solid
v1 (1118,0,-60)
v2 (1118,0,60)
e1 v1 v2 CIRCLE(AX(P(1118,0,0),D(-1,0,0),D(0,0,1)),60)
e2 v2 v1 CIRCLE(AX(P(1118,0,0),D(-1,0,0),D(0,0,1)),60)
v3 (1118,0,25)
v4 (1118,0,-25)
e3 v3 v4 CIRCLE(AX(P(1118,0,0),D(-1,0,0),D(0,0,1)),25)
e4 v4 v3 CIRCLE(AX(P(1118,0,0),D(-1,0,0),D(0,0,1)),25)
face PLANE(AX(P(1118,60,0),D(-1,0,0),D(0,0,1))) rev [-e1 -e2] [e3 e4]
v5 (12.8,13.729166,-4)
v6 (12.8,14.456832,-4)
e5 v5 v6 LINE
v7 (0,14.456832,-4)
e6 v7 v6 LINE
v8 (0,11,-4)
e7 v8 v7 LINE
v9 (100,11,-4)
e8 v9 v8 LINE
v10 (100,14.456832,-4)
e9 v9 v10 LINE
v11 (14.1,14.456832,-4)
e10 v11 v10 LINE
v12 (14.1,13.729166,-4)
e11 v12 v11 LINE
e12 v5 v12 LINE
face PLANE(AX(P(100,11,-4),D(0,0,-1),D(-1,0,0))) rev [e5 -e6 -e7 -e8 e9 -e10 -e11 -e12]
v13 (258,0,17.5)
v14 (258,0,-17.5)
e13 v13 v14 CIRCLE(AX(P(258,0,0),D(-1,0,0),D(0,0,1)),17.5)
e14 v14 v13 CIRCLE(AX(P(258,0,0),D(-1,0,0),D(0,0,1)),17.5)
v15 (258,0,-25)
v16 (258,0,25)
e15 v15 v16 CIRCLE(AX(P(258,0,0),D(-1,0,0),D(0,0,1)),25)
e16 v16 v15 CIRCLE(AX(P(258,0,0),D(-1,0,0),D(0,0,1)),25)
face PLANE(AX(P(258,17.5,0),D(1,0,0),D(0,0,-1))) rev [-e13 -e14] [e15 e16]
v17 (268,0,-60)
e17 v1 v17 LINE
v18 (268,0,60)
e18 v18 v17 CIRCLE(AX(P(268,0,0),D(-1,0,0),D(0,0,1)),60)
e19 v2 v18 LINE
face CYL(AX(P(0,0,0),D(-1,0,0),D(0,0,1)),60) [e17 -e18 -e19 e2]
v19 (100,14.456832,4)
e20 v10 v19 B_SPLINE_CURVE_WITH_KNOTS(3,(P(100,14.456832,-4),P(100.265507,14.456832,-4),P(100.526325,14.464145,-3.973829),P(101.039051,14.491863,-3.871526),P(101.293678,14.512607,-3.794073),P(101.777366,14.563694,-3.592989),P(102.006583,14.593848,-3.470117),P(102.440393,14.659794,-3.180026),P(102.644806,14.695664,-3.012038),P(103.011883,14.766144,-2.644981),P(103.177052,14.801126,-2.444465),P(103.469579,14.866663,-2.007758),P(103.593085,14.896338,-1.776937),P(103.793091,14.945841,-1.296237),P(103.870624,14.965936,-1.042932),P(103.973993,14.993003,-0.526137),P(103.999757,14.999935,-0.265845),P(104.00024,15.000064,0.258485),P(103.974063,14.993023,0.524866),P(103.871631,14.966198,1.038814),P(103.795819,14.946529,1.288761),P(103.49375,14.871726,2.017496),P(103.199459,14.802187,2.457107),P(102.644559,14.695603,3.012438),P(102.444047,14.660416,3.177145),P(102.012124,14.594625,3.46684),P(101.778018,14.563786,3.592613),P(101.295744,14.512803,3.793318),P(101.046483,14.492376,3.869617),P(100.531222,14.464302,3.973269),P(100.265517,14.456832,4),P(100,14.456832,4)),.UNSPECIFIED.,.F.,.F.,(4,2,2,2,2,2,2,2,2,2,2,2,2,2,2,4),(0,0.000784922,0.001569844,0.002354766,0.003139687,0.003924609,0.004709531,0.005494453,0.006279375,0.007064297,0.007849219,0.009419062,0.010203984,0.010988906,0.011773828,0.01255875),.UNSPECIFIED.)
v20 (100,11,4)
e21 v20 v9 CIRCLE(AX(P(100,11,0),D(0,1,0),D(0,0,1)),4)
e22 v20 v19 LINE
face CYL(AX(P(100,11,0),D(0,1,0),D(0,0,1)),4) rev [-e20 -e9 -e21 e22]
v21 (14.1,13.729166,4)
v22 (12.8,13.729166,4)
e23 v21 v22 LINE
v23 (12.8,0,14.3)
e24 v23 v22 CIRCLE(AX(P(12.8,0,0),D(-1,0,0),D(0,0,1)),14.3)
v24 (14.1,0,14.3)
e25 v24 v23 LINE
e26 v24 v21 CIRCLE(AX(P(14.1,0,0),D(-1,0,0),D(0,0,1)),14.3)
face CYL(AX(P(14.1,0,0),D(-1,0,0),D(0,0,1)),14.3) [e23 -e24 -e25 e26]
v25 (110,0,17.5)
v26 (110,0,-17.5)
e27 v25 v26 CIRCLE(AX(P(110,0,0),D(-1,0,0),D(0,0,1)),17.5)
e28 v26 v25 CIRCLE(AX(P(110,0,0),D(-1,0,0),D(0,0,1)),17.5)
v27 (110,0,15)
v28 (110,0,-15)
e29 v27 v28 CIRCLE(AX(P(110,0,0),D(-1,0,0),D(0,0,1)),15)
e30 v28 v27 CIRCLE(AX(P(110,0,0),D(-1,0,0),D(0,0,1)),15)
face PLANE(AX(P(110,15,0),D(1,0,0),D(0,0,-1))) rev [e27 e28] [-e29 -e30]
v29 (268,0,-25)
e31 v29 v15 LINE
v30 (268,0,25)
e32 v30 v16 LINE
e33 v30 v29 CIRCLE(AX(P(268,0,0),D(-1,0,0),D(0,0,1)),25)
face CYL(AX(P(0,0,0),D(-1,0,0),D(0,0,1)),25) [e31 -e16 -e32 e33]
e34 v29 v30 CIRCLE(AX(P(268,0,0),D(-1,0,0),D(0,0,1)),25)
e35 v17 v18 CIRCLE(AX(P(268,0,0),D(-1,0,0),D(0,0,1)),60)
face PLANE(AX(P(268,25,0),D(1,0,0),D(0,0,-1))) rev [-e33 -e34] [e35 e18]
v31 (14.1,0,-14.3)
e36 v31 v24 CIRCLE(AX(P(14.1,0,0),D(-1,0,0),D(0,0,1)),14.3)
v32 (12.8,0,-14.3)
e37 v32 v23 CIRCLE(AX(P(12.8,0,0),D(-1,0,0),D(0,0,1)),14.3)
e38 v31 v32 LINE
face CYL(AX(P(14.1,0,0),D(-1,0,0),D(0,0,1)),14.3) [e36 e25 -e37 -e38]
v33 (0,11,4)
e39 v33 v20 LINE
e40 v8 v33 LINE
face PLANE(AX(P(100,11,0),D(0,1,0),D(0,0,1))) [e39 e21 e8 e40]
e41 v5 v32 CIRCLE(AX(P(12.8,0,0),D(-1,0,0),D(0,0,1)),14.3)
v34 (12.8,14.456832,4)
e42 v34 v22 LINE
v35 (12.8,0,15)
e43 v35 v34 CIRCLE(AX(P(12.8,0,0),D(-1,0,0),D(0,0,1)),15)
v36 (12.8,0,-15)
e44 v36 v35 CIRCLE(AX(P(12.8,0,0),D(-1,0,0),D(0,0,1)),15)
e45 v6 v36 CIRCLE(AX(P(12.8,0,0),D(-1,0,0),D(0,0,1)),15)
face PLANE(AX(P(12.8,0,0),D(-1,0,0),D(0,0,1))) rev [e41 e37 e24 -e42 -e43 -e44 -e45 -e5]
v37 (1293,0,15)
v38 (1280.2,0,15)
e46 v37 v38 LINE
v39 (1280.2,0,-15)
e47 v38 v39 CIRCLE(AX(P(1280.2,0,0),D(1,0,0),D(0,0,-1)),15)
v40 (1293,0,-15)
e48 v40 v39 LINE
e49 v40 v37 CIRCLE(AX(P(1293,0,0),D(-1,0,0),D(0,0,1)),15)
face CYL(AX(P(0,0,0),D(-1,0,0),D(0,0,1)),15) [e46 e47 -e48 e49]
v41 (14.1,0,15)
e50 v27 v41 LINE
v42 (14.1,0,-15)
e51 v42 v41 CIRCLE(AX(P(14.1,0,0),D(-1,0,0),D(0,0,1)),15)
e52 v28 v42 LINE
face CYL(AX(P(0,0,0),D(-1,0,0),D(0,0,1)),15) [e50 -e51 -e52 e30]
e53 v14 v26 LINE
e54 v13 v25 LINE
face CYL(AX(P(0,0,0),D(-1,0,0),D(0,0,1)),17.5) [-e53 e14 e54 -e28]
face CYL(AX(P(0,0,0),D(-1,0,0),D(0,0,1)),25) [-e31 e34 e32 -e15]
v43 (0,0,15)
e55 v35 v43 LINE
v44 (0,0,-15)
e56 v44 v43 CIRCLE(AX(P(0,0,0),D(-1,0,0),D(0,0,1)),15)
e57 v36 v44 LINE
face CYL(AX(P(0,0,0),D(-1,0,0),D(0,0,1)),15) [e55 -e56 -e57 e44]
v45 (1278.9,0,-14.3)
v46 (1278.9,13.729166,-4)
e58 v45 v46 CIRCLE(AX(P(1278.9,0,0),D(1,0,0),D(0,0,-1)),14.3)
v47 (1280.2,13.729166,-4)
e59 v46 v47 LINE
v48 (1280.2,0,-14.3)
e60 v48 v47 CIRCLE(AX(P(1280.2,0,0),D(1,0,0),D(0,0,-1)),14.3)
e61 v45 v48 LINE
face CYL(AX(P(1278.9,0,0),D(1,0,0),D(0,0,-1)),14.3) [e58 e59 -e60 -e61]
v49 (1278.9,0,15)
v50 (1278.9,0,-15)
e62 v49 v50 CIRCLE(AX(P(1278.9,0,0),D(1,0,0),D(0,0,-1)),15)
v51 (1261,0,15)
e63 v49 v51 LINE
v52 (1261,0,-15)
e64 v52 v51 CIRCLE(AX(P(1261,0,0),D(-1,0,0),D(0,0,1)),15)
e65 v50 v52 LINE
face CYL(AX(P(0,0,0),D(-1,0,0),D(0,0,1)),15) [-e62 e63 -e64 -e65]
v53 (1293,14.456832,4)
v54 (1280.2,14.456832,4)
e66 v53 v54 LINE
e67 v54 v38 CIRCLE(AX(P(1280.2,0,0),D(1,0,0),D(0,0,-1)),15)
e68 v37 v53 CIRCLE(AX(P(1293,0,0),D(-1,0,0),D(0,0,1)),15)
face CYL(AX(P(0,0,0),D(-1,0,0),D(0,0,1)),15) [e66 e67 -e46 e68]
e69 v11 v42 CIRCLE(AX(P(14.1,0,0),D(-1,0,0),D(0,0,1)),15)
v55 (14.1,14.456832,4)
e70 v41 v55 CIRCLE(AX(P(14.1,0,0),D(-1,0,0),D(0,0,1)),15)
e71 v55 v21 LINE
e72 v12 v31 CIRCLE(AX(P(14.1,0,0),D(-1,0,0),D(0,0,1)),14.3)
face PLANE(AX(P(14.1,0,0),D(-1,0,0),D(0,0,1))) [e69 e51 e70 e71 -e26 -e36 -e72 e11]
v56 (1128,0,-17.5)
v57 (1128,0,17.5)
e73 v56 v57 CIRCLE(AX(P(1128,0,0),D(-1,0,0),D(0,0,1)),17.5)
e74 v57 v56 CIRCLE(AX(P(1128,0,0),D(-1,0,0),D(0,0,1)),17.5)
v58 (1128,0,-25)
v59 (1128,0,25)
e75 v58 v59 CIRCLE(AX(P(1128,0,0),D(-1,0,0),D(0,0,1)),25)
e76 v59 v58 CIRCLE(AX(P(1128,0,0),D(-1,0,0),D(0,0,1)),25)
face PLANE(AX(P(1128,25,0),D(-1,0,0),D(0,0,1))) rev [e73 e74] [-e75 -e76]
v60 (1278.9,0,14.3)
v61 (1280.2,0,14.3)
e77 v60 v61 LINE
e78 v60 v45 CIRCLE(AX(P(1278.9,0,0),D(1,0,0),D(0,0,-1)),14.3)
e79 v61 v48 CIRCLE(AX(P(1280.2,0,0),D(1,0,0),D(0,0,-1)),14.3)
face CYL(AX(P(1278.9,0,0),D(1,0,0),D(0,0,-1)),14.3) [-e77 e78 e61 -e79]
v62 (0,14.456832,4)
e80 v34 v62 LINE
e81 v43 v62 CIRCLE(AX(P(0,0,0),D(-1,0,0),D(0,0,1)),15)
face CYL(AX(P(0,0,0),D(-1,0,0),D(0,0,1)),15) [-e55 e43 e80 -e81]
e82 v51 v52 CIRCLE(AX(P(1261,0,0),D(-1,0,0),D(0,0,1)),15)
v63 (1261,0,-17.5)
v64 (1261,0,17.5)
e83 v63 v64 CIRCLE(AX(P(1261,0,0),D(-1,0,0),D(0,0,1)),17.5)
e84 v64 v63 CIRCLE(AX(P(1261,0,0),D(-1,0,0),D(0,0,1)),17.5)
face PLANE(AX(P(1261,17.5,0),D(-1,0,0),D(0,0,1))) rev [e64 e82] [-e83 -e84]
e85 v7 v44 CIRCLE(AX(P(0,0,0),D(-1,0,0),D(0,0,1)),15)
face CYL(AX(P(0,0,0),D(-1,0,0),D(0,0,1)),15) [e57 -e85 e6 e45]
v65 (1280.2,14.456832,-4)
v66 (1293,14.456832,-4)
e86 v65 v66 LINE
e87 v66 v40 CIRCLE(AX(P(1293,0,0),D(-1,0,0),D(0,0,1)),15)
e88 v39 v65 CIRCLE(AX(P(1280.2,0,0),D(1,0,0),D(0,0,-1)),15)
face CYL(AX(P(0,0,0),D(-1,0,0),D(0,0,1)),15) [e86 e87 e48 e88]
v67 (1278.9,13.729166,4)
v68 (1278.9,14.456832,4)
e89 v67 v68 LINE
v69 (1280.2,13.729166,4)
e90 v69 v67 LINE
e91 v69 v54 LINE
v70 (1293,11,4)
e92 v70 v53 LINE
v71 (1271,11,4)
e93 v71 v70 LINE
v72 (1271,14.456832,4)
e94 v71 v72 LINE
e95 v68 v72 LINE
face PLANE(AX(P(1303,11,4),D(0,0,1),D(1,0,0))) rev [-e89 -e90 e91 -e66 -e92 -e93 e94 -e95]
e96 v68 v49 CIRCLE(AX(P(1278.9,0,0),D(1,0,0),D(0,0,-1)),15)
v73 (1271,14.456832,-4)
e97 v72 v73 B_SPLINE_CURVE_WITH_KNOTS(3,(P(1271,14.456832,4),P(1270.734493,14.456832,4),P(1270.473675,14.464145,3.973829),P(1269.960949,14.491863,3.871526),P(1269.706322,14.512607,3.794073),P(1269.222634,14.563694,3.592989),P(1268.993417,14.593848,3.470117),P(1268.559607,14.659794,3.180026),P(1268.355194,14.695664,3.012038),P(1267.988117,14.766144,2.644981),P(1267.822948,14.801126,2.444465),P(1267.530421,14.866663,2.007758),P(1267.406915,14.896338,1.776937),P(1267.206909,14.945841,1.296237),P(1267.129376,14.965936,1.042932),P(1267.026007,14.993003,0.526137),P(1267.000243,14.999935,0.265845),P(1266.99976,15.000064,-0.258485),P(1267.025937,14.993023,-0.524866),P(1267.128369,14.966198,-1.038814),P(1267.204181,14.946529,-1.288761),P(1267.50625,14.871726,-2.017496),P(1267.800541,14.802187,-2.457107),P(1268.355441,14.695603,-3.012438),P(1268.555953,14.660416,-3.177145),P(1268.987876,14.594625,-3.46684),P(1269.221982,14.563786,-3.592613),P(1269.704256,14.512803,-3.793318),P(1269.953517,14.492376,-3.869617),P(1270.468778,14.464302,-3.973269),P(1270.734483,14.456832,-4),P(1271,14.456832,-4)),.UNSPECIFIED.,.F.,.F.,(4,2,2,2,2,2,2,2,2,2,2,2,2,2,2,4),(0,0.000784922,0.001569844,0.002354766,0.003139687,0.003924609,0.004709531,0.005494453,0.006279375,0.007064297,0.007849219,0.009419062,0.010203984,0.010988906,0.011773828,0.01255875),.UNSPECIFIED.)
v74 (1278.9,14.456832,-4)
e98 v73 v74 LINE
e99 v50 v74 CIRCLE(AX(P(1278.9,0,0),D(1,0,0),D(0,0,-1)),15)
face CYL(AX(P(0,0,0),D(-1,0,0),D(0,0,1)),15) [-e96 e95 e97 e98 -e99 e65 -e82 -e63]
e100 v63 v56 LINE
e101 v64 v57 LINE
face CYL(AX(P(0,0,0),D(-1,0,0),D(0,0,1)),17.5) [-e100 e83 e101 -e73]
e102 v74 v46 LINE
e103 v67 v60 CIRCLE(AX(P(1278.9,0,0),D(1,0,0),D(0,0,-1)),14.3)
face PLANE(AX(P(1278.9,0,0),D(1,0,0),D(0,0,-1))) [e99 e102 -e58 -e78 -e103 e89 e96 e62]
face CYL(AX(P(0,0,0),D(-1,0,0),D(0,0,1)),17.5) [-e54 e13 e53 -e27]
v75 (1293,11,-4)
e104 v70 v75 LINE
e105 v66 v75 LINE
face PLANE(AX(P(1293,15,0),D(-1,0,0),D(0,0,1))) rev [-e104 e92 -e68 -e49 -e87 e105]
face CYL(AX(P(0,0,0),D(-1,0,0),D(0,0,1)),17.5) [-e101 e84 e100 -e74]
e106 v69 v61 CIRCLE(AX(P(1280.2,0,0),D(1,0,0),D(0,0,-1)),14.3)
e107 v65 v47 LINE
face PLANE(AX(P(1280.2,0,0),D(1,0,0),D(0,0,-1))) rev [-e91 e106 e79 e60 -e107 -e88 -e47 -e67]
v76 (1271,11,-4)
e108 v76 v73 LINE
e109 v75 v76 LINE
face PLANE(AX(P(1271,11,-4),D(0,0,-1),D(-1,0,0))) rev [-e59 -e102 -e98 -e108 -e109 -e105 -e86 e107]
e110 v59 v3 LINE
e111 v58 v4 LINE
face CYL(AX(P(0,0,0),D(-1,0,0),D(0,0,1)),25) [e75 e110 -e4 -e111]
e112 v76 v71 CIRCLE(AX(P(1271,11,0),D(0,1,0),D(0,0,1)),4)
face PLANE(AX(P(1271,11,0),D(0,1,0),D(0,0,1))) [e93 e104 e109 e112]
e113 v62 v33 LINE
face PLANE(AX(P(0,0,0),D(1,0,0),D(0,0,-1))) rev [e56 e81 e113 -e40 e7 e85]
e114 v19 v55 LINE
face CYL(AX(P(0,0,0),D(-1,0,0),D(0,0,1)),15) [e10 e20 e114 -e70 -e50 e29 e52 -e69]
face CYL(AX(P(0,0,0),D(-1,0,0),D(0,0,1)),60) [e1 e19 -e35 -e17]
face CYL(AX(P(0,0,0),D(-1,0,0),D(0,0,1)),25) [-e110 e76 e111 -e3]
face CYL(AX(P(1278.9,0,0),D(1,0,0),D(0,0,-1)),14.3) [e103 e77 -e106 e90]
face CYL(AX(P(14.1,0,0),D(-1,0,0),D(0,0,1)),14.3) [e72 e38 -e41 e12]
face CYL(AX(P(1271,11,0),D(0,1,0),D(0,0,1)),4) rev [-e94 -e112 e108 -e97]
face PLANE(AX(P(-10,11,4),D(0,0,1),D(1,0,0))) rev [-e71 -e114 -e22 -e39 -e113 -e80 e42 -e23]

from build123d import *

# Parameters (mm, degrees)
CUT_EXTRUDE_1_DEPTH = 4
CUT_EXTRUDE_START   = -1.3
SKETCH_3_R          = 15
SKETCH_3_R_2        = 14.3
CUT_EXTRUDE_2_DEPTH = 1.3
CUT_EXTRUDE_3_DEPTH = 4
SKETCH_5_R          = 15
SKETCH_5_R_2        = 14.3
CUT_EXTRUDE_4_DEPTH = 1.3


with BuildPart() as part:
    # 草图1 → 旋转1 (revolve)
    with BuildSketch(Plane.XY, mode=Mode.PRIVATE) as revolve_1_sk:
        Polygon((0, 0), (0, 15), (110, 15), (110, 17.5), (258, 17.5), (258, 25), (268, 25), (268, 60), (1118, 60), (1118, 25), (1128, 25), (1128, 17.5), (1261, 17.5), (1261, 15), (1293, 15), (1293, 0), align=None)
    revolve(revolve_1_sk.sketch.rotate(Axis((0, 0, 0), (1, 0, 0)), 90), axis=Axis((0, 0, 0), (1, 0, 0)))

    # 草图2 → 切除-拉伸1 (cut)
    with BuildSketch(Plane(origin=(0, 15, 0), x_dir=(1, 0, 0), z_dir=(0, 1, 0))):
        with BuildLine():
            Line((100, 4), (-10, 4))
            Line((-10, 4), (-10, -4))
            Line((-10, -4), (100, -4))
            ThreePointArc((100, -4), (104, 0), (100, 4))
        make_face()
    extrude(amount=-CUT_EXTRUDE_1_DEPTH, mode=Mode.SUBTRACT)

    # 草图3 → 切除-拉伸2 (cut)
    with BuildSketch(Plane.ZY.offset(-12.8).offset(CUT_EXTRUDE_START)):
        Circle(SKETCH_3_R)
        Circle(SKETCH_3_R_2, mode=Mode.SUBTRACT)
    extrude(amount=CUT_EXTRUDE_2_DEPTH, mode=Mode.SUBTRACT)

    # 草图4 → 切除-拉伸3 (cut)
    with BuildSketch(Plane(origin=(0, 15, 0), x_dir=(1, 0, 0), z_dir=(0, 1, 0))):
        with BuildLine():
            Line((1271, 4), (1303, 4))
            Line((1303, 4), (1303, -4))
            Line((1303, -4), (1271, -4))
            ThreePointArc((1271, -4), (1267, 0), (1271, 4))
        make_face()
    extrude(amount=-CUT_EXTRUDE_3_DEPTH, mode=Mode.SUBTRACT)

    # 草图5 → 切除-拉伸4 (cut)
    with BuildSketch(Plane(origin=(1280.2, 0, 0), x_dir=(0, 0, -1), z_dir=(1, 0, 0))):
        with Locations(Location((0, 0, 0), (0, 0, 180))):
            Circle(SKETCH_5_R)
        Circle(SKETCH_5_R_2, mode=Mode.SUBTRACT)
    extrude(amount=-CUT_EXTRUDE_4_DEPTH, mode=Mode.SUBTRACT)


solid = part.part
